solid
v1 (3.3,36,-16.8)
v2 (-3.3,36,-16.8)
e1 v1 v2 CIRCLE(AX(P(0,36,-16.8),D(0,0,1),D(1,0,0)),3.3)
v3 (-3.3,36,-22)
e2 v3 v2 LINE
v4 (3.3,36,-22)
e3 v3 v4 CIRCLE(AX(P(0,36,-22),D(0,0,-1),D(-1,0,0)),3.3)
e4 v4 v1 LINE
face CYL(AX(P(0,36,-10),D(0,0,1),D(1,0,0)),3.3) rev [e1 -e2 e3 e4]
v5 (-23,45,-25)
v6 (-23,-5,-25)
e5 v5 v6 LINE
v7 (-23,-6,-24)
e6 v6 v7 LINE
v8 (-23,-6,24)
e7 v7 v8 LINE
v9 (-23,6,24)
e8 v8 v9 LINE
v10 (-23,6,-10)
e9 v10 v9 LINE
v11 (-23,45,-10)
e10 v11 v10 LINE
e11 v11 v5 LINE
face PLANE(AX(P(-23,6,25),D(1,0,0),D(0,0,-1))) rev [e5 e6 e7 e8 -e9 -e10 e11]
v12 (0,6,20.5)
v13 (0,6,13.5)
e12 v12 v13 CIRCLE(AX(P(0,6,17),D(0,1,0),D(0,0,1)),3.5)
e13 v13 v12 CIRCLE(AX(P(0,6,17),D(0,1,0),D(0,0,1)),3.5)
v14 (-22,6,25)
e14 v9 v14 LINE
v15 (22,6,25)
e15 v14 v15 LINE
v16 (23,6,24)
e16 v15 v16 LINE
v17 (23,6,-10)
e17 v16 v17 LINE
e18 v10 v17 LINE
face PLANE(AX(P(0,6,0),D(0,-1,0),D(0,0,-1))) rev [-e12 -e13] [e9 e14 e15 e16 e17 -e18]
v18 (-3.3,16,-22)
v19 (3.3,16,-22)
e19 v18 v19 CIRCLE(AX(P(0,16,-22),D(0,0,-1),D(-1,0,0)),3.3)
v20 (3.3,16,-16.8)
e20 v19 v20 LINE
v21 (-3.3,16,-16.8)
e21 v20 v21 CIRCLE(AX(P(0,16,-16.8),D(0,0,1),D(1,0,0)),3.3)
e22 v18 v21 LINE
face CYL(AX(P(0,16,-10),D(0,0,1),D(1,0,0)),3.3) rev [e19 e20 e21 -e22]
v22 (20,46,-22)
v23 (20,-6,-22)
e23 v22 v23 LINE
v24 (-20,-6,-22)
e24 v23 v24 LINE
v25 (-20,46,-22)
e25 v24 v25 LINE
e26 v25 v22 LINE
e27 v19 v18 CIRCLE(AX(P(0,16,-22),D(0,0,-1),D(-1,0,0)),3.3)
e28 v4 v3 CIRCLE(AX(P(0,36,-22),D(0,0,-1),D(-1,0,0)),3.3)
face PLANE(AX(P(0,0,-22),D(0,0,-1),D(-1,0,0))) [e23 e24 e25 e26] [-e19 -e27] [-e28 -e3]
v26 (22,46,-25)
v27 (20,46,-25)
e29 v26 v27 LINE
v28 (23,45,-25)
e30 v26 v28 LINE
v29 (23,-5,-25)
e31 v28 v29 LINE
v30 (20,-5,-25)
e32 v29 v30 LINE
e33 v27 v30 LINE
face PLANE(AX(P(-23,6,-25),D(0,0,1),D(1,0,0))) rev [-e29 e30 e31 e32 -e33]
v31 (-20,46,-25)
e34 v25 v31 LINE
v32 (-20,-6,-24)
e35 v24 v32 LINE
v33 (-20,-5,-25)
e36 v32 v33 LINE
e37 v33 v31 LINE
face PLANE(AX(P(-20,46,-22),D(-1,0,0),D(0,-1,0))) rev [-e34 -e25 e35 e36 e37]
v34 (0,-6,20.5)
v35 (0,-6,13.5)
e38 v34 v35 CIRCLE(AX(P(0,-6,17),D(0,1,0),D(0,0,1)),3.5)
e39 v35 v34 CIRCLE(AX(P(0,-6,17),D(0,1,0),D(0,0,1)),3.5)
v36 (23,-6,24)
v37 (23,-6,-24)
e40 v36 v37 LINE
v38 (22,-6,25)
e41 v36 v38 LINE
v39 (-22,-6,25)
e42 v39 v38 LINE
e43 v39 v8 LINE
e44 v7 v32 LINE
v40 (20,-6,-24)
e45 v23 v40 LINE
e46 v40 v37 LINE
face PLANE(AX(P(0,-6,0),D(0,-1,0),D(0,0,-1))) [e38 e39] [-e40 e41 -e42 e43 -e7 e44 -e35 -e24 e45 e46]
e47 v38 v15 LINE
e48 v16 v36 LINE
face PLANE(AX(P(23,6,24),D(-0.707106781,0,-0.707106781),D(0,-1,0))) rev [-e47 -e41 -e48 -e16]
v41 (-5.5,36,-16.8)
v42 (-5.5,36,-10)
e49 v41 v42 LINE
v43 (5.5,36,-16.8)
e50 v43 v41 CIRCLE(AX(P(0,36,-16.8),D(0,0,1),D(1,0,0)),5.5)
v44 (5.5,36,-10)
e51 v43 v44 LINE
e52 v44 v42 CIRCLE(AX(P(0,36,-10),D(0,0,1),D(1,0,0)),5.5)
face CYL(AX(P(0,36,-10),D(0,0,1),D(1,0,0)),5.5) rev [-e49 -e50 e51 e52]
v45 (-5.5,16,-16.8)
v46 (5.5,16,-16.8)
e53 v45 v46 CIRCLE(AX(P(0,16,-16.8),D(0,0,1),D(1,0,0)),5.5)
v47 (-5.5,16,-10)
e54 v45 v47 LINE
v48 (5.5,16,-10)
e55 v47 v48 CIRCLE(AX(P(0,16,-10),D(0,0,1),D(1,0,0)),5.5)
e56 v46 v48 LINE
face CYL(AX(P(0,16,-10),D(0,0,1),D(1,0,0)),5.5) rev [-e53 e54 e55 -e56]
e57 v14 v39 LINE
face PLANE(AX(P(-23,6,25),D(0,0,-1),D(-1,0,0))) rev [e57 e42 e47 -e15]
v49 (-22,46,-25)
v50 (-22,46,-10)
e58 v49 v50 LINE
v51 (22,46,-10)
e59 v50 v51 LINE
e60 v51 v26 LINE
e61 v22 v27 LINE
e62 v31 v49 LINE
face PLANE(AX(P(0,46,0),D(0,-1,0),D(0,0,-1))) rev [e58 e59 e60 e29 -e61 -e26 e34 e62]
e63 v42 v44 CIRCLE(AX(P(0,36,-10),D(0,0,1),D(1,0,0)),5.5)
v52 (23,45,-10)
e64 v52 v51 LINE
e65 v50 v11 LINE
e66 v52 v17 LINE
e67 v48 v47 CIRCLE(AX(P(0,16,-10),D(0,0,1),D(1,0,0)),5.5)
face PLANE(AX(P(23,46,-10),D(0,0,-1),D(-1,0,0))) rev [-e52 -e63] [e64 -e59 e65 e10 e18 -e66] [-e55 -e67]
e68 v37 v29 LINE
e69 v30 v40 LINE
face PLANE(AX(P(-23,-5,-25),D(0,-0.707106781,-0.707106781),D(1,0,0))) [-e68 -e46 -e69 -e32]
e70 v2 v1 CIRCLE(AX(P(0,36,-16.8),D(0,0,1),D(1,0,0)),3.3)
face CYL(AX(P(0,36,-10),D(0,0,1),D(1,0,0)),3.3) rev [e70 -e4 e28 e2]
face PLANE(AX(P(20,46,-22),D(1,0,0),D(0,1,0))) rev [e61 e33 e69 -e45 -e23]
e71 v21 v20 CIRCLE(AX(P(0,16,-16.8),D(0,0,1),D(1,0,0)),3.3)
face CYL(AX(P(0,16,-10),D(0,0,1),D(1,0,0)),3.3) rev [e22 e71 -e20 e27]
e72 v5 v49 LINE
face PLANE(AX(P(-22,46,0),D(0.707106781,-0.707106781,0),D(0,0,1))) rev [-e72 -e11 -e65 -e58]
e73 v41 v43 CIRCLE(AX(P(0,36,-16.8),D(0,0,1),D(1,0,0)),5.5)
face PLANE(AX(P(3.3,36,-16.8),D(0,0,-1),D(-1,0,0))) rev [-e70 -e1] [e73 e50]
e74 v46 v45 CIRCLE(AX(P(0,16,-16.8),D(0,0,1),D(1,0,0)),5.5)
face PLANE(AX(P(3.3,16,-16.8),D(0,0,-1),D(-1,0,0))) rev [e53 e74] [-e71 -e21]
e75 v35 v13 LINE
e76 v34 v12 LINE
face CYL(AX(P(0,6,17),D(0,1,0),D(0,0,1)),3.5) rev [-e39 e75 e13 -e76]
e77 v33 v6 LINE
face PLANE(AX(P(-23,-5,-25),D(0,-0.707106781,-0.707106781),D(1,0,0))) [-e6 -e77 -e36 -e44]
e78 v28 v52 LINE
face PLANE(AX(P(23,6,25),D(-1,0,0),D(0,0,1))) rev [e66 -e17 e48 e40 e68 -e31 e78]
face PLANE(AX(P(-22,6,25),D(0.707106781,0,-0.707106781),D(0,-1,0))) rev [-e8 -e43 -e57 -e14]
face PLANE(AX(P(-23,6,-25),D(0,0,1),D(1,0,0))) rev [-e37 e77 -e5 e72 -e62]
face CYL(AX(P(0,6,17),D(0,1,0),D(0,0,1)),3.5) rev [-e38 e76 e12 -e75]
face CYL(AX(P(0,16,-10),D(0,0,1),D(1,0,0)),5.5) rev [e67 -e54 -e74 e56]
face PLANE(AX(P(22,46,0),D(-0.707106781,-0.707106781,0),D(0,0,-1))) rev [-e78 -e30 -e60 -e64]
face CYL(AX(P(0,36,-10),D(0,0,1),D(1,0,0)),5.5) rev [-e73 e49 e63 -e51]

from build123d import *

# Parameters (mm, degrees)
SKETCH_1_W                = 46
SKETCH_1_H                = 50
EXTRUDE_1_DEPTH           = 6
SKETCH_2_W                = 46
SKETCH_2_H                = 15
EXTRUDE_2_DEPTH           = 40
SKETCH_3_W                = 40
SKETCH_3_H                = 52
CUT_EXTRUDE_1_DEPTH       = 3
CHAMFER_1_SIZE            = 1
HOLE_WIZARD_1_D           = 6.6
HOLE_WIZARD_1_CBORE_D     = 11
HOLE_WIZARD_1_CBORE_DEPTH = 6.8
M8X1_0_1_D                = 7


with BuildPart() as part:
    # 草图1 → 凸台-拉伸1 (new, symmetric)
    with BuildSketch(Plane(origin=(0, 0, 0), x_dir=(1, 0, 0), z_dir=(0, 1, 0))):
        Rectangle(SKETCH_1_W, SKETCH_1_H)
    extrude(amount=EXTRUDE_1_DEPTH, both=True)

    # 草图2 → 凸台-拉伸2 (add)
    with BuildSketch(Plane(origin=(0, 6, 0), x_dir=(1, 0, 0), z_dir=(0, 1, 0))):
        with Locations((0, 17.5)):
            Rectangle(SKETCH_2_W, SKETCH_2_H)
    extrude(amount=EXTRUDE_2_DEPTH)

    # 草图3 → 切除-拉伸1 (cut)
    with BuildSketch(Plane(origin=(0, 0, -25), x_dir=(-1, 0, 0), z_dir=(0, 0, -1))):
        with Locations((0, 20)):
            Rectangle(SKETCH_3_W, SKETCH_3_H)
    extrude(amount=-CUT_EXTRUDE_1_DEPTH, mode=Mode.SUBTRACT)

    # 倒角1
    chamfer_1_edges = [part.edges().sort_by_distance(p)[0] for p in [
        (23, 46, -17.5),
        (-23, 46, -17.5),
        (-21.5, -6, -25),
        (21.5, -6, -25),
        (23, 0, 25),
        (-23, 0, 25),
    ]]
    chamfer(chamfer_1_edges, length=CHAMFER_1_SIZE)

    # 打孔尺寸(%根据)内六角圆柱头螺钉的类型1 (through all)
    with Locations(Plane.XY.offset(-10)):
        with Locations((0, 16), (0, 36)):
            CounterBoreHole(HOLE_WIZARD_1_D / 2, HOLE_WIZARD_1_CBORE_D / 2, HOLE_WIZARD_1_CBORE_DEPTH)

    # M8x1.0 螺纹孔1 (through all)
    with Locations(Plane(origin=(0, 6, 0), x_dir=(1, 0, 0), z_dir=(0, 1, 0))):
        with Locations((0, -17)):
            Hole(M8X1_0_1_D / 2)


solid = part.part
